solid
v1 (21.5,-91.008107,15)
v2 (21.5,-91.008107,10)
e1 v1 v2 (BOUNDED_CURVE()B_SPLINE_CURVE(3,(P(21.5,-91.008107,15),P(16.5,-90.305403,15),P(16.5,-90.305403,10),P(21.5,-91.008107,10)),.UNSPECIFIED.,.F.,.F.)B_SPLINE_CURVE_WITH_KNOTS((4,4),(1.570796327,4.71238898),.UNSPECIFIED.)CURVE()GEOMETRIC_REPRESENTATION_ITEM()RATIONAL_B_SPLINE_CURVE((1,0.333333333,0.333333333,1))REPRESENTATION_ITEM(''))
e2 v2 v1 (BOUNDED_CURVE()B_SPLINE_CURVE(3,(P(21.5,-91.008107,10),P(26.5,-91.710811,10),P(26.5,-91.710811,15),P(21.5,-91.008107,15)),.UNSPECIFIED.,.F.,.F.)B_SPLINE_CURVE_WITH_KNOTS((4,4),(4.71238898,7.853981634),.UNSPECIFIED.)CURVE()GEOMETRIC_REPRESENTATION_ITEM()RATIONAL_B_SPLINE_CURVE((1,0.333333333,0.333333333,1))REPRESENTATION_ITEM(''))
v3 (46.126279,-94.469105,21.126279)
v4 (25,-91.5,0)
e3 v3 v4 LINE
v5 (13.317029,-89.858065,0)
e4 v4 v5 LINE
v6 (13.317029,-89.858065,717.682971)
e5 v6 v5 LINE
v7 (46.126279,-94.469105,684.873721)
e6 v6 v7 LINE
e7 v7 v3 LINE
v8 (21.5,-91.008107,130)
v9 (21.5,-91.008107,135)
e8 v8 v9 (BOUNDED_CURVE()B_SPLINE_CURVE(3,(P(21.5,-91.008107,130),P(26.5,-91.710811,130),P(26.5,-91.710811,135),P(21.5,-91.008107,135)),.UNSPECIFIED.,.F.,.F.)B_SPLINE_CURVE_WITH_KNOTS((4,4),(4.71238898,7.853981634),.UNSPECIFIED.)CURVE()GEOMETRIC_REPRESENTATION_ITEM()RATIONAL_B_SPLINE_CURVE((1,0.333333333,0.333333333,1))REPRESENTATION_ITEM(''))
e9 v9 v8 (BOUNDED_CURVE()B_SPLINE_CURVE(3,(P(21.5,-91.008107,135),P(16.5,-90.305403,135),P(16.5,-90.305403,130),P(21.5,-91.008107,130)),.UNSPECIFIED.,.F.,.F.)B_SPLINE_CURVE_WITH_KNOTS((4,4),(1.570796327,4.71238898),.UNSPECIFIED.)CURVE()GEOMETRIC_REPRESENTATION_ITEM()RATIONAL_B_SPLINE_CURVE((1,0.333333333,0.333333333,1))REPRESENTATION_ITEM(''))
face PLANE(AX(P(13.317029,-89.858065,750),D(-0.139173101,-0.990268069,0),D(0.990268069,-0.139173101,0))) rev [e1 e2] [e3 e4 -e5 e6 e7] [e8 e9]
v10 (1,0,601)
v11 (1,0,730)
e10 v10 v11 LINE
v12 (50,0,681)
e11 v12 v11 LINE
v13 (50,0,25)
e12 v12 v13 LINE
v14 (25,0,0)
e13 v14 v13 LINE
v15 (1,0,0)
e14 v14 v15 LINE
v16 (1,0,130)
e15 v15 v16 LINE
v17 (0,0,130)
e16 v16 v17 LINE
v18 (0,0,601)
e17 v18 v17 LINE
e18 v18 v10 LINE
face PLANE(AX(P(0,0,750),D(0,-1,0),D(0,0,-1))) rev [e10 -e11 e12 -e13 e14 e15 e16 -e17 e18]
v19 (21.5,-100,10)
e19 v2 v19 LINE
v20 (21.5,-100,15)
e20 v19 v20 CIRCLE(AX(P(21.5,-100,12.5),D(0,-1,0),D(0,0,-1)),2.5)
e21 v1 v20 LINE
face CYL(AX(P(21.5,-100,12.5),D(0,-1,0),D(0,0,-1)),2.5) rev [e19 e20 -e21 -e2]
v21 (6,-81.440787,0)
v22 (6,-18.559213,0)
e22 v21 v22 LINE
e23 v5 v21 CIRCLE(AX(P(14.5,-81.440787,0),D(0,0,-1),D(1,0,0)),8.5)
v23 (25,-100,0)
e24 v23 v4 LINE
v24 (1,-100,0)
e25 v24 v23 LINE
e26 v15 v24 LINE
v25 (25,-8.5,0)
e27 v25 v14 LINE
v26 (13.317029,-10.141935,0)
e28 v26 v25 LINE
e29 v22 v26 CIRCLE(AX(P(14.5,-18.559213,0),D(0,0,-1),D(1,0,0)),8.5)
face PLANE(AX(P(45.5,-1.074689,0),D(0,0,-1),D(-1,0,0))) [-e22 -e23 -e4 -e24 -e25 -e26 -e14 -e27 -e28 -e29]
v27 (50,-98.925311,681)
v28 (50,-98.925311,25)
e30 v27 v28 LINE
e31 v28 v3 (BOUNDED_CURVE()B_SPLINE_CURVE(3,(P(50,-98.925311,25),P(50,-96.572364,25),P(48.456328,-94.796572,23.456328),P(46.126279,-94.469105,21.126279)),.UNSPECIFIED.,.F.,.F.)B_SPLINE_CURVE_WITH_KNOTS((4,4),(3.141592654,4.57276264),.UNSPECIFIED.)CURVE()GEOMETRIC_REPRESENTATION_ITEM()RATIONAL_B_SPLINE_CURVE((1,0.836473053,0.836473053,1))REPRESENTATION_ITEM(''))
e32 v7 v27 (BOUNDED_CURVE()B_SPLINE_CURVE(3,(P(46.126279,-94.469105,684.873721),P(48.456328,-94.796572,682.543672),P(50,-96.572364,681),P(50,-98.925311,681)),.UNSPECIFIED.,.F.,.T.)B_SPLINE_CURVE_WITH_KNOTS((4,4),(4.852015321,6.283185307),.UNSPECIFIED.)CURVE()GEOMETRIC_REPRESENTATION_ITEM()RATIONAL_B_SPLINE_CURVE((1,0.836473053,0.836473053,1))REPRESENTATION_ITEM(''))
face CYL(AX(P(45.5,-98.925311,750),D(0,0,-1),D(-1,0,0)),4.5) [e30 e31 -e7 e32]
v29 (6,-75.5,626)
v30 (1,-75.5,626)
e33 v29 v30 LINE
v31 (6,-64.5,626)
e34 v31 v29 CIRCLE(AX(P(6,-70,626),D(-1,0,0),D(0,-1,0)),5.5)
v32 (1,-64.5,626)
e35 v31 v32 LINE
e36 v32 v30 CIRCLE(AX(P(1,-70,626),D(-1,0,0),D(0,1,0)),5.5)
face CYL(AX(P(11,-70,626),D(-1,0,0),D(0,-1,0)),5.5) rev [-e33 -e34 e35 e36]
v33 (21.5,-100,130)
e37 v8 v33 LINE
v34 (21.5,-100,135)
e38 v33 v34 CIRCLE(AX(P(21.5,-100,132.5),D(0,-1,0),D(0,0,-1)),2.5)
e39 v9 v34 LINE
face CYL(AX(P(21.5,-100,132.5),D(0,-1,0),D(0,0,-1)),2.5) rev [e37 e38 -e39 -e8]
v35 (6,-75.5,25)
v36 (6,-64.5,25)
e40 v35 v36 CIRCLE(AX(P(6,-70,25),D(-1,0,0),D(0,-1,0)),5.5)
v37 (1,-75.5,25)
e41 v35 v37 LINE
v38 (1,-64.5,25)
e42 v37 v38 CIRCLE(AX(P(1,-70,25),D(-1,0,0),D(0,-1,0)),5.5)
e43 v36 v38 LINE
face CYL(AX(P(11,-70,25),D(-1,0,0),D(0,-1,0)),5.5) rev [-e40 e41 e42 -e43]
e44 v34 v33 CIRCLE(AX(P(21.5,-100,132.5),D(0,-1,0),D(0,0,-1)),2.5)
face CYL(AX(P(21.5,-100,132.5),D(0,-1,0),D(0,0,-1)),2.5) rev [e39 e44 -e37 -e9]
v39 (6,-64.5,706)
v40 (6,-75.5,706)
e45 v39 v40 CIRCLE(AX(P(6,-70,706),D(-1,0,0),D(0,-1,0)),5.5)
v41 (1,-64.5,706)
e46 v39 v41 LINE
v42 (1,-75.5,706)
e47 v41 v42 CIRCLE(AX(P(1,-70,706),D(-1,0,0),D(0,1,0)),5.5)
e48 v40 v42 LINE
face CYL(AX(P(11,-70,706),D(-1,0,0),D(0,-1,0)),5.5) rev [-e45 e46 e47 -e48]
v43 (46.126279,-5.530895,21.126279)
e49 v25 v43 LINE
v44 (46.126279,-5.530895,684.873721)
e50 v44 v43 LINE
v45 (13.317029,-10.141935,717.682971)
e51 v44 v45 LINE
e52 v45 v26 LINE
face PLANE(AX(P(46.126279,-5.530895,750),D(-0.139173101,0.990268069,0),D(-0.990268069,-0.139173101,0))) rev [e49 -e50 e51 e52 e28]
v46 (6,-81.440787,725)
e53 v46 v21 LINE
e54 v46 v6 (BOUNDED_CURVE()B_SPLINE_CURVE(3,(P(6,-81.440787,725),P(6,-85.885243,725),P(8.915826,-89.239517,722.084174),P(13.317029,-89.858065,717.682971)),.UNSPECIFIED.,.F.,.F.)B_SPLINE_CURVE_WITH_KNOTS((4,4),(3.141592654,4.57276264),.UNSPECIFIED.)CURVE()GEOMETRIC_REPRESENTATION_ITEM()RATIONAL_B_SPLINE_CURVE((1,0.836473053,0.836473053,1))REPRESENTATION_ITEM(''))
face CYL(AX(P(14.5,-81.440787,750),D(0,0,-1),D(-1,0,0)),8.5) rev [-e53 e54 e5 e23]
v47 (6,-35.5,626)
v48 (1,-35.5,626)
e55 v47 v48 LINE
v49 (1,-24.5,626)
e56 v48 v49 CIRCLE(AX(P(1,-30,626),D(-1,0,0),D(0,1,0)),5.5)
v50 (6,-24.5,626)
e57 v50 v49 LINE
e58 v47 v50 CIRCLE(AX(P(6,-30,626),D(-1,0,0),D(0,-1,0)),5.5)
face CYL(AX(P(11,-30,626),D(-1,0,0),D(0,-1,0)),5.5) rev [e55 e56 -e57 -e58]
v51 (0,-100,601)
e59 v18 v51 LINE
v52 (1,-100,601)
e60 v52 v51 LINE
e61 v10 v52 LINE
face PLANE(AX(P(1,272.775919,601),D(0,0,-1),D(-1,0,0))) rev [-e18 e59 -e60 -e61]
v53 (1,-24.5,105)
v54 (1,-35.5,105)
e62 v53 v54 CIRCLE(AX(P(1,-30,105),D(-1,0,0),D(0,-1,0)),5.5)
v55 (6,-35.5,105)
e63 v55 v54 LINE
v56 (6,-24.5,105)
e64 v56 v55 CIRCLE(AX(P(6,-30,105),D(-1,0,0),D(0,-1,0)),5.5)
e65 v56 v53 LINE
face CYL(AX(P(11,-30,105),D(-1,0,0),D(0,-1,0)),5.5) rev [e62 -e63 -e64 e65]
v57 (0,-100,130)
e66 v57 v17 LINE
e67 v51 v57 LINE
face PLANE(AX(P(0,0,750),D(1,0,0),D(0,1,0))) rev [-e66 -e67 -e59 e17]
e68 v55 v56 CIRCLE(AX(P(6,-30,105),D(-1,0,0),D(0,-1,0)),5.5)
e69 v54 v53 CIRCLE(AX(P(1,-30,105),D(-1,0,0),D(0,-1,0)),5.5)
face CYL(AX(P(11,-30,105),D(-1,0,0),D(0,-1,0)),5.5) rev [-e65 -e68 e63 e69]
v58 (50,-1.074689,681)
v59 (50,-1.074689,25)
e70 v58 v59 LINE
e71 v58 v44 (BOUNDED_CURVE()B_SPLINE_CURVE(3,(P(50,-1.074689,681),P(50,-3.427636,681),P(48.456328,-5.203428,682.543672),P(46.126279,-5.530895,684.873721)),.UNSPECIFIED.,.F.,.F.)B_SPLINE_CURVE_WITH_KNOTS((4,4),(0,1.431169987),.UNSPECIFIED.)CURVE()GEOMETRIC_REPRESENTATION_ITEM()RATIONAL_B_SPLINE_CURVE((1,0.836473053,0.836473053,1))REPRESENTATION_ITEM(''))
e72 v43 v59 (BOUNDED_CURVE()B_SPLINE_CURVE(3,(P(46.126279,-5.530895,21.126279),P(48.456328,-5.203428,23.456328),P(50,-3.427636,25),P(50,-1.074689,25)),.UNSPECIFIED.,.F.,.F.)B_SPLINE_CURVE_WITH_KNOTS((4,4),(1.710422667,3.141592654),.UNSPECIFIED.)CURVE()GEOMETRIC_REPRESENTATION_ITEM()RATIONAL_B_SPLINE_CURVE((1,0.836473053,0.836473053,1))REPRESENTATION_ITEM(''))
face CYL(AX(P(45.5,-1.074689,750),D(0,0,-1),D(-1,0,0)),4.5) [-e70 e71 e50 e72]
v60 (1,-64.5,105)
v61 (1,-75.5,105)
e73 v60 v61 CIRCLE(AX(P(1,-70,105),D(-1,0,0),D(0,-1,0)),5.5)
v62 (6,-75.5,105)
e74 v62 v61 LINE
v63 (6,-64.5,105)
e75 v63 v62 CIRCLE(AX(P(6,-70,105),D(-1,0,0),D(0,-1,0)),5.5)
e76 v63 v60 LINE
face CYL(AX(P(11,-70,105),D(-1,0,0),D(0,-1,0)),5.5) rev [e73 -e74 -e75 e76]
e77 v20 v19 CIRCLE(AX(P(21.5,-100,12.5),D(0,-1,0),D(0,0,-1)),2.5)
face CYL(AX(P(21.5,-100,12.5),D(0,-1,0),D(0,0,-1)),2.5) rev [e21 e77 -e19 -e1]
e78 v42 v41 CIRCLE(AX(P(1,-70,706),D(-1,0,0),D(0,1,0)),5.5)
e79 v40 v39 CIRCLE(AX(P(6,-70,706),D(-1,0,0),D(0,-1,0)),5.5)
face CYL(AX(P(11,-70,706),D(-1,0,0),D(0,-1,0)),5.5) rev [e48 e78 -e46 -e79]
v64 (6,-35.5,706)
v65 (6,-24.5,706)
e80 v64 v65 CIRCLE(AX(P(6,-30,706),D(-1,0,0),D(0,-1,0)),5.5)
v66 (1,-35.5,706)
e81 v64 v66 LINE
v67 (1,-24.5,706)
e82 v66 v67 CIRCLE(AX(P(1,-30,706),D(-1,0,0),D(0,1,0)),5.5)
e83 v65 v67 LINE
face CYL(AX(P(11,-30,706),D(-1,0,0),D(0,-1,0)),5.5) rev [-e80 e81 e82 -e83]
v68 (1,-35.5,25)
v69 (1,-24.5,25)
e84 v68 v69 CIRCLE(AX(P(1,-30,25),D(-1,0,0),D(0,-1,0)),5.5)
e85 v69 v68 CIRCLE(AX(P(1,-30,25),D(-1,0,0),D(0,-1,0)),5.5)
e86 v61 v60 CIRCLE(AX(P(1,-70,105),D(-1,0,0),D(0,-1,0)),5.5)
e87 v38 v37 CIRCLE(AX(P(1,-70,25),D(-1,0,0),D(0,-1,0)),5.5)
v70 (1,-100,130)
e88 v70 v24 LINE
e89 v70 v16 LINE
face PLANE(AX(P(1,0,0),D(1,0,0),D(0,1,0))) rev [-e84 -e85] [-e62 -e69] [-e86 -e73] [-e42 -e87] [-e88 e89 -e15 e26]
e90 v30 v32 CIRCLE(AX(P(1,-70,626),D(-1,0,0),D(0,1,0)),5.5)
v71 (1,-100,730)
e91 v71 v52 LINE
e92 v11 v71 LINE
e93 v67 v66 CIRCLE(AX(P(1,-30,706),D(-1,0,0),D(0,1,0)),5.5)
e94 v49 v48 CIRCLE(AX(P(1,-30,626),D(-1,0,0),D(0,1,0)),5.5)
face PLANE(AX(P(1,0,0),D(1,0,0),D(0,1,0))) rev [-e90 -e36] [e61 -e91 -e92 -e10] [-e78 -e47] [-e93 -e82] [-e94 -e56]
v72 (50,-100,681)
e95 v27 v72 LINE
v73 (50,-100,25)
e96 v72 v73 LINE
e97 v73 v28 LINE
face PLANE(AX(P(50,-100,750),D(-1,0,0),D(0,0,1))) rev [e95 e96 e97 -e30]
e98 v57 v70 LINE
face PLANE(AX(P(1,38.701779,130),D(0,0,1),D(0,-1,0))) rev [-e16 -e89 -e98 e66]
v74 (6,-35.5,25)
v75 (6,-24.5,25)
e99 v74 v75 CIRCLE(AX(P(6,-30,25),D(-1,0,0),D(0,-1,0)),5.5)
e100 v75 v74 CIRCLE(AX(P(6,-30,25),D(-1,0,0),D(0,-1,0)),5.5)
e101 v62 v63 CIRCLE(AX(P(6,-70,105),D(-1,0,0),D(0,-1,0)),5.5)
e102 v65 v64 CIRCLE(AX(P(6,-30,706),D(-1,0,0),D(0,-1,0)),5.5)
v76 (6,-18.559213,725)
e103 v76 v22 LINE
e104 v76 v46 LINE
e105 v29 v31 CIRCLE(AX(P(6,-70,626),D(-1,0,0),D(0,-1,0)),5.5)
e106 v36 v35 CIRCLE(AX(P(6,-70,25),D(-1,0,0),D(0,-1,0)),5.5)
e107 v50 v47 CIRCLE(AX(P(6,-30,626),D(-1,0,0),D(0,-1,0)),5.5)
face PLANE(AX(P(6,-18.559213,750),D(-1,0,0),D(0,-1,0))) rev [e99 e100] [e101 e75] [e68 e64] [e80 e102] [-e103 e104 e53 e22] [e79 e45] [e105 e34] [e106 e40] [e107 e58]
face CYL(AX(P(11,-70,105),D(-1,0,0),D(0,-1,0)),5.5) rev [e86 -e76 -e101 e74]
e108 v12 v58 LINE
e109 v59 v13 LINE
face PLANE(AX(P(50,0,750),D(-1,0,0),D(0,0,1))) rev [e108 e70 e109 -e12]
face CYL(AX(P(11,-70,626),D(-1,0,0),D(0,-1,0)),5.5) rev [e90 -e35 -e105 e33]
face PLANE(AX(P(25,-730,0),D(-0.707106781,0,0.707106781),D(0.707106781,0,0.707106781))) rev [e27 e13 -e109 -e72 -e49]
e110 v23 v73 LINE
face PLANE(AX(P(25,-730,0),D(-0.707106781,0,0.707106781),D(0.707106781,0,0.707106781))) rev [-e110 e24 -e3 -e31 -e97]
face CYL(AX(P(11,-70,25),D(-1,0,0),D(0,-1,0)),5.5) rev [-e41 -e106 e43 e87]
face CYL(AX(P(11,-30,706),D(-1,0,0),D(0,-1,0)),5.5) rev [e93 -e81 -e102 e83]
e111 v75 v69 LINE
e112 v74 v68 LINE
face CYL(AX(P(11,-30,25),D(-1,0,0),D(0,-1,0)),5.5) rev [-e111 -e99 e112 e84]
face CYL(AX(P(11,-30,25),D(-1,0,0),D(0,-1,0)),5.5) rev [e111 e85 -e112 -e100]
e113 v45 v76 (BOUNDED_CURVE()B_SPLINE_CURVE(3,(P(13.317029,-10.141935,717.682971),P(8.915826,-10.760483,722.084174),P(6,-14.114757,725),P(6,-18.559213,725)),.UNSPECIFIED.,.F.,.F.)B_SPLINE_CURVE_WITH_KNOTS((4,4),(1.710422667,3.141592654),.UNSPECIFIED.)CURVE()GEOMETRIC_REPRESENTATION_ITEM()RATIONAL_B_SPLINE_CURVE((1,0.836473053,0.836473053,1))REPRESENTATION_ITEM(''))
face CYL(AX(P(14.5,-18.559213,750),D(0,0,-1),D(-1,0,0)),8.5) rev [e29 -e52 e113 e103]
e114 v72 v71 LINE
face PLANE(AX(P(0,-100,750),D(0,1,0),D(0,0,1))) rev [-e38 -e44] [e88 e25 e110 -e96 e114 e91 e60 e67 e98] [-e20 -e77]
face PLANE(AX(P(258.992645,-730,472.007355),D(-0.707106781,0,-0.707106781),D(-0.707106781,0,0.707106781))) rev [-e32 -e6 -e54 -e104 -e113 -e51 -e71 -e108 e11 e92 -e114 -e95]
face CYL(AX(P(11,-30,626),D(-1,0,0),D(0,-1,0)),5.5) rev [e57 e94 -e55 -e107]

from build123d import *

# Parameters (mm, degrees)
BOSS_EXTRUDE1_DEPTH   = 750
CUT_EXTRUDE1_DEPTH    = 730
SKETCH3_W             = 246.792493201
SKETCH3_H             = 411.477698095
CUT_EXTRUDE2_DEPTH    = 1
SKETCH4_R             = 5.5
CUT_EXTRUDE3_DEPTH    = 10
M6_TAPPED_HOLE1_D     = 5
M6_TAPPED_HOLE1_DEPTH = 15
M6_TAPPED_HOLE1_TIP   = 1.502151548
M6_TAPPED_HOLE2_D     = 5
M6_TAPPED_HOLE2_DEPTH = 15
M6_TAPPED_HOLE2_TIP   = 1.502151548


with BuildPart() as part:
    # Sketch1 → Boss-Extrude1 (new body)
    with BuildSketch(Plane.XY):
        with BuildLine():
            Line((0, 0), (0, -100))
            Line((0, -100), (50, -100))
            Line((50, -100), (50, -98.925311188))
            ThreePointArc((50, -98.925311188), (48.896193111, -95.973045557), (46.126278954, -94.469104878))
            Line((46.126278954, -94.469104878), (13.317028642, -89.858065454))
            ThreePointArc((13.317028642, -89.858065454), (8.084968568, -87.017288616), (6, -81.440786869))
            Line((6, -81.440786869), (6, -18.559213131))
            ThreePointArc((6, -18.559213131), (8.084968568, -12.982711384), (13.317028642, -10.141934546))
            Line((13.317028642, -10.141934546), (46.126278954, -5.530895122))
            ThreePointArc((46.126278954, -5.530895122), (48.896193111, -4.026954443), (50, -1.074688812))
            Line((50, -1.074688812), (50, 0))
            Line((50, 0), (0, 0))
        make_face()
    extrude(amount=BOSS_EXTRUDE1_DEPTH)

    # Sketch2 → Cut-Extrude1 (cut)
    with BuildSketch(Plane(origin=(0, 0, 0), x_dir=(1, 0, 0), z_dir=(0, 1, 0))):
        Polygon((258.992644717, -472.007355283), (0, -731), (-59.777153602, -772.262203455), (30.841373369, -818.159898935), (45.044802943, -785.872759949), (459.456990019, -587.675626999), align=None)
        Polygon((25, 0), (50, -25), (50, 48.41721094), align=None)
    extrude(amount=-CUT_EXTRUDE1_DEPTH, mode=Mode.SUBTRACT)

    # Sketch3 → Cut-Extrude2 (cut)
    with BuildSketch(Plane.ZY):
        Polygon((130, 38.70177923), (130, -162.725177772), (-125.633599865, -119.606257313), (-100.418312462, 29.884375145), align=None)
        with Locations((724.396246601, 67.037069817)):
            Rectangle(SKETCH3_W, SKETCH3_H)
    extrude(amount=-CUT_EXTRUDE2_DEPTH, mode=Mode.SUBTRACT)

    # Sketch4 → Cut-Extrude3 (cut)
    with BuildSketch(Plane.ZY.offset(-1)):
        with Locations(Location((25, -30, 0), (0, 0, 270))):
            Circle(SKETCH4_R)
        with Locations(Location((105, -30, 0), (0, 0, 270))):
            Circle(SKETCH4_R)
        with Locations(Location((25, -70, 0), (0, 0, 270))):
            Circle(SKETCH4_R)
        with Locations(Location((105, -70, 0), (0, 0, 270))):
            Circle(SKETCH4_R)
        with Locations(Location((626, -30, 0), (0, 0, 270))):
            Circle(SKETCH4_R)
        with Locations(Location((706, -70, 0), (0, 0, 270))):
            Circle(SKETCH4_R)
        with Locations(Location((626, -70, 0), (0, 0, 270))):
            Circle(SKETCH4_R)
        with Locations(Location((706, -30, 0), (0, 0, 270))):
            Circle(SKETCH4_R)
    extrude(amount=-CUT_EXTRUDE3_DEPTH, mode=Mode.SUBTRACT)

    # M6 Tapped Hole1
    with Locations(Plane(origin=(0, -100, 0), x_dir=(-1, 0, 0), z_dir=(0, -1, 0))):
        with Locations((-21.5, -12.5)):
            Hole(M6_TAPPED_HOLE1_D / 2, depth=M6_TAPPED_HOLE1_DEPTH)
            with Locations((0, 0, -(M6_TAPPED_HOLE1_DEPTH + M6_TAPPED_HOLE1_TIP / 2))):  # 118° drill point
                Cone(0, M6_TAPPED_HOLE1_D / 2, M6_TAPPED_HOLE1_TIP, mode=Mode.SUBTRACT)

    # M6 Tapped Hole2
    with Locations(Plane(origin=(0, -100, 0), x_dir=(-1, 0, 0), z_dir=(0, -1, 0))):
        with Locations((-21.5, -132.5)):
            Hole(M6_TAPPED_HOLE2_D / 2, depth=M6_TAPPED_HOLE2_DEPTH)
            with Locations((0, 0, -(M6_TAPPED_HOLE2_DEPTH + M6_TAPPED_HOLE2_TIP / 2))):  # 118° drill point
                Cone(0, M6_TAPPED_HOLE2_D / 2, M6_TAPPED_HOLE2_TIP, mode=Mode.SUBTRACT)


solid = part.part
